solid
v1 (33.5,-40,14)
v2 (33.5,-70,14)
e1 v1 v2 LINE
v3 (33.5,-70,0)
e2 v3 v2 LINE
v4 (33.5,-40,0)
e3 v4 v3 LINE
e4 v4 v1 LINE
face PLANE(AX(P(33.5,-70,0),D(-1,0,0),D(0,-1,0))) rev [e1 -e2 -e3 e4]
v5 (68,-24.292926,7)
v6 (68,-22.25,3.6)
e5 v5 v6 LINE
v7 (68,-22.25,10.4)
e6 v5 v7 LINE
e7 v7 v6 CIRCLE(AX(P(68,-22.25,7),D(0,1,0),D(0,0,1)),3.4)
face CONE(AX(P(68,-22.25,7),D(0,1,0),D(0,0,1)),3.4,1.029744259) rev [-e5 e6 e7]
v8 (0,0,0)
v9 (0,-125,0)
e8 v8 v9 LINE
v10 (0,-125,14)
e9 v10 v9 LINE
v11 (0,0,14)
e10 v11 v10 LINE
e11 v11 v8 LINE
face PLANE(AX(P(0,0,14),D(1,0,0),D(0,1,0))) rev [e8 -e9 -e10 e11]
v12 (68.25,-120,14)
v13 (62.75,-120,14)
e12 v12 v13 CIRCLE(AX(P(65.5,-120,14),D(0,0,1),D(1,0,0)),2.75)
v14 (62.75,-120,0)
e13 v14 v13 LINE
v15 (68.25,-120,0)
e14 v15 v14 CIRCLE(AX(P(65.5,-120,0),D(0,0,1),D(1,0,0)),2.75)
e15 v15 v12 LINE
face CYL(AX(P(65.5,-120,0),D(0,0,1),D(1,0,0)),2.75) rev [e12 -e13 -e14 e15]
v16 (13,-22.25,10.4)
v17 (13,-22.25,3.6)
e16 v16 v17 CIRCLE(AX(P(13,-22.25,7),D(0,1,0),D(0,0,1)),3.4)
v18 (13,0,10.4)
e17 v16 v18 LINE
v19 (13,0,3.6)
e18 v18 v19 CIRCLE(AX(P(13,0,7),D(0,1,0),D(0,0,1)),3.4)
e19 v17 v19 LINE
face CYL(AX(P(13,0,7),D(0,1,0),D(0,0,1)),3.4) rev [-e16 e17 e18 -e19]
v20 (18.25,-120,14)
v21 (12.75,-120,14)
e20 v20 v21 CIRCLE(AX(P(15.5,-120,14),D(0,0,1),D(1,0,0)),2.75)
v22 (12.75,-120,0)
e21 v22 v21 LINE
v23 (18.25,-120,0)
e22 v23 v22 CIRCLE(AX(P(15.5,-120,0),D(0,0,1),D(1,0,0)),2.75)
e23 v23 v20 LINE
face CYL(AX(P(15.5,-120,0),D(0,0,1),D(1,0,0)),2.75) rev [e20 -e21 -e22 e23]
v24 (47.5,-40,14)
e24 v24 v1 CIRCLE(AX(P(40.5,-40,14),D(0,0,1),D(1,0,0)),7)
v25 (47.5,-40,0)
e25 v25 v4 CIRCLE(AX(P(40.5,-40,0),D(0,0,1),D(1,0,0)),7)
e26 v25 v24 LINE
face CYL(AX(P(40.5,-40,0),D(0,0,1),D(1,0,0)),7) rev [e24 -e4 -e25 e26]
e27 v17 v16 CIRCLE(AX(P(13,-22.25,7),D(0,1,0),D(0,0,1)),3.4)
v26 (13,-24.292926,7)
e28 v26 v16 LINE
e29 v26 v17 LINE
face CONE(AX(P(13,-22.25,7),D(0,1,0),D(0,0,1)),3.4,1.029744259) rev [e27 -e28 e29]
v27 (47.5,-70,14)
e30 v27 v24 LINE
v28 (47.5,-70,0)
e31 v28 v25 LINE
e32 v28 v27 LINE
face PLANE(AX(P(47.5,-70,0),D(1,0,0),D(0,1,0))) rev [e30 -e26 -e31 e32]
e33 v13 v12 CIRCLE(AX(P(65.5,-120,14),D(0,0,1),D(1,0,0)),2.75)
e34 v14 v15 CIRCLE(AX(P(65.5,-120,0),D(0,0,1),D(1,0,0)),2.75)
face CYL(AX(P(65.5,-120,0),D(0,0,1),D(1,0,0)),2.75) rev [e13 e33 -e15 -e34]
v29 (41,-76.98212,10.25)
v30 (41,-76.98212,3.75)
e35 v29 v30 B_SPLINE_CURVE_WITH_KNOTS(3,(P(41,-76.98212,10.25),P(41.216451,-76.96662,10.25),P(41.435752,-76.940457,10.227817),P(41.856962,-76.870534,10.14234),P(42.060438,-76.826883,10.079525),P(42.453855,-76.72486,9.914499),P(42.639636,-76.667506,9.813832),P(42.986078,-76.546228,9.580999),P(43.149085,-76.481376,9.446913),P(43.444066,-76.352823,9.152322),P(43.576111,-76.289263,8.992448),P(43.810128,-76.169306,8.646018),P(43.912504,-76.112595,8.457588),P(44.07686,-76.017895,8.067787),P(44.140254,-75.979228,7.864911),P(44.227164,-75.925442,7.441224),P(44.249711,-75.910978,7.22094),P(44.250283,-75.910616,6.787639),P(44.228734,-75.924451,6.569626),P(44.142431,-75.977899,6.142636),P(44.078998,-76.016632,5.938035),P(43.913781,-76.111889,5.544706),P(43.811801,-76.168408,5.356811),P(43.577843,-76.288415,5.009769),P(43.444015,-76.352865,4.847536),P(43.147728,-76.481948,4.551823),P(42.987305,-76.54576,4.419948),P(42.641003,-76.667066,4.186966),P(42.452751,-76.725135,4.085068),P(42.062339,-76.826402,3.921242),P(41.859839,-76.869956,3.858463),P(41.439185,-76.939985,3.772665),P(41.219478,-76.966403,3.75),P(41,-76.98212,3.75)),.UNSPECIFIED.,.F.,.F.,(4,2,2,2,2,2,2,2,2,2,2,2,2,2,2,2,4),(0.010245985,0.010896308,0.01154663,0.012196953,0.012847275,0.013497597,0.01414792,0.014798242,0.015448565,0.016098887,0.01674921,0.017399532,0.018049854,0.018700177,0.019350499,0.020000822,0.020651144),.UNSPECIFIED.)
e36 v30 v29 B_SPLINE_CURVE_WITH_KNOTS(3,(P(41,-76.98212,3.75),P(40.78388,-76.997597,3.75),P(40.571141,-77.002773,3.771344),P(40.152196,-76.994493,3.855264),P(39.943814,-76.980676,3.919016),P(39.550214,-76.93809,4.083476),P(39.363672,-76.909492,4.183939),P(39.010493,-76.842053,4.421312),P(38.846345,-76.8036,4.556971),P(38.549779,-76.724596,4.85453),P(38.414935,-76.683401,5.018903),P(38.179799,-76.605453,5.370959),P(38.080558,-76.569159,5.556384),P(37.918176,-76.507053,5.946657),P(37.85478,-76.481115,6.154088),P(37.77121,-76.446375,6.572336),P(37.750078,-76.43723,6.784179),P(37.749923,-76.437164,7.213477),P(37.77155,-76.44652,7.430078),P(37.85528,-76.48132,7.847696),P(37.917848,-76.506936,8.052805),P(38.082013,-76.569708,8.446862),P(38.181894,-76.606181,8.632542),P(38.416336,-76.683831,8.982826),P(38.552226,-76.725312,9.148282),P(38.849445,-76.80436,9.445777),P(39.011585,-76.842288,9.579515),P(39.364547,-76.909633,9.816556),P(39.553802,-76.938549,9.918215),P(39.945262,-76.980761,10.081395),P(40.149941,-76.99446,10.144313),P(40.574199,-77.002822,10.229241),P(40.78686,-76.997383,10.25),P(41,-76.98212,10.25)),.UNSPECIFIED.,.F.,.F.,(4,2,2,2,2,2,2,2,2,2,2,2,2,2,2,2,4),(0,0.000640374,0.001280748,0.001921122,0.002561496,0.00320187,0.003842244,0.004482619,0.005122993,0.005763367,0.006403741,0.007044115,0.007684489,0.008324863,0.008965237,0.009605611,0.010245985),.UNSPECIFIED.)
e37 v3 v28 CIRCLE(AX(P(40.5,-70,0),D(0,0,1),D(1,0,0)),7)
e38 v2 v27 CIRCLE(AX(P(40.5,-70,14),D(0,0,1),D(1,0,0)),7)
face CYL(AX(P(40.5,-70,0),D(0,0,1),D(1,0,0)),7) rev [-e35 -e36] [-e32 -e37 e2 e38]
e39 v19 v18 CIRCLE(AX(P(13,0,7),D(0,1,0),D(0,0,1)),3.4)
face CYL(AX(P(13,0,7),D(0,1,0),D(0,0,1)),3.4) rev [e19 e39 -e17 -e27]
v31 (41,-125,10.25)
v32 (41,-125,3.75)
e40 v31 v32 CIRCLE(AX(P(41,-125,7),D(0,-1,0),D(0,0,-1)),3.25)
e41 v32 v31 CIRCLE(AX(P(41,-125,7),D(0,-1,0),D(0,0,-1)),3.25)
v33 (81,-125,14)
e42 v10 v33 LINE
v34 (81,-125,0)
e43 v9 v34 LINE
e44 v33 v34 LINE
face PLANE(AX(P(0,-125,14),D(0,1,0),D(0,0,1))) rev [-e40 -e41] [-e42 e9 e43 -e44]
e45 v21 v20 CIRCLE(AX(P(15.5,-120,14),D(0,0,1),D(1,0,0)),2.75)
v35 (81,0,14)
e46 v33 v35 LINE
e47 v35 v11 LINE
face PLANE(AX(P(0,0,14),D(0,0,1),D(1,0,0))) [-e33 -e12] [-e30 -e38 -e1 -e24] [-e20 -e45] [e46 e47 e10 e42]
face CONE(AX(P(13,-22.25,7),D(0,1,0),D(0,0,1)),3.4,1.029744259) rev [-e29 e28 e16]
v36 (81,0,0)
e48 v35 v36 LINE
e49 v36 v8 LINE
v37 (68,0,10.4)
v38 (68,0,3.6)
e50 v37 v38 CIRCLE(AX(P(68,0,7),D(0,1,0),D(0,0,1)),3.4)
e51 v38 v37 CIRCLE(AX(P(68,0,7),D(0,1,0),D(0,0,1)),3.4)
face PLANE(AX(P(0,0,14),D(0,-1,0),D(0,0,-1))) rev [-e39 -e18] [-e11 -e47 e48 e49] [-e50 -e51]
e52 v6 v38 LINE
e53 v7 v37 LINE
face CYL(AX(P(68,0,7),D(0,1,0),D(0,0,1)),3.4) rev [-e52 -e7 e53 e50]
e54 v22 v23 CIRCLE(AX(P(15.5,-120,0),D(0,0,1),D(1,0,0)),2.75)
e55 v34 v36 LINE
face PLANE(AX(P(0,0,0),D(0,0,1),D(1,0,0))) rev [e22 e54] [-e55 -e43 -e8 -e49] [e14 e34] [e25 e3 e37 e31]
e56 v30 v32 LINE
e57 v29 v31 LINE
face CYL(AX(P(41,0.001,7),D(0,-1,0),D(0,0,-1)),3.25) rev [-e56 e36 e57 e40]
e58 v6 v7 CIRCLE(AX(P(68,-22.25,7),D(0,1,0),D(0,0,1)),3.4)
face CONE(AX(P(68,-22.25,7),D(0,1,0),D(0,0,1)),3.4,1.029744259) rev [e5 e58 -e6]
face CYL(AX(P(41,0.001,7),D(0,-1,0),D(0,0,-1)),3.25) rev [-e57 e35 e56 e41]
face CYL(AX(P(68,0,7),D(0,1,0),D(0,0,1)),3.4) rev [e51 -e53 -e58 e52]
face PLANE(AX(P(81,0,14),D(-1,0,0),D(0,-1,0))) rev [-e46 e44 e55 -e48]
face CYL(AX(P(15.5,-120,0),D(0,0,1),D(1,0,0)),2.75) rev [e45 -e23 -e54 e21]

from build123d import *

# Parameters (mm, degrees)
SKETCH_1_W               = 81
SKETCH_1_H               = 125
EXTRUDE_1_DEPTH          = 14
CUT_EXTRUDE_1_DEPTH      = 150.606149606
CUT_EXTRUDE_2_REACH      = 145.948
CUT_EXTRUDE_2_END_RADIUS = 7
SKETCH_4_R               = 3.25
HOLE_WIZARD_M8_1_D       = 6.8
HOLE_WIZARD_M8_1_DEPTH   = 22.25
HOLE_WIZARD_M8_1_TIP     = 2.042926105
SKETCH_11_R              = 2.75
CUT_EXTRUDE_3_DEPTH      = 150.606149699


with BuildPart() as part:
    # 草图1 → 凸台-拉伸1 (new body)
    with BuildSketch(Plane.XY):
        with Locations((40.5, -62.5)):
            Rectangle(SKETCH_1_W, SKETCH_1_H)
    extrude(amount=EXTRUDE_1_DEPTH)

    # 草图2 → 切除-拉伸1 (cut, through all)
    with BuildSketch(Plane.XY.offset(14)):
        with BuildLine():
            Line((33.5, -70), (33.5, -40))
            ThreePointArc((33.5, -40), (40.5, -33), (47.5, -40))
            Line((47.5, -40), (47.5, -70))
            ThreePointArc((47.5, -70), (40.5, -77), (33.5, -70))
        make_face()
    extrude(amount=-CUT_EXTRUDE_1_DEPTH, mode=Mode.SUBTRACT)

    # 切除-拉伸2: up to this cylinder (the profile starts outside it)
    cut_extrude_2_end = Plane(origin=(40.5, -70, 7), z_dir=(0, 0, 1)) * Cylinder(CUT_EXTRUDE_2_END_RADIUS, 306.896, mode=Mode.PRIVATE)
    # 草图4 → 切除-拉伸2 (cut, up to the surface)
    with BuildSketch(Plane(origin=(70, -125, 0), x_dir=(0, 0, -1), z_dir=(0, -1, 0)), mode=Mode.PRIVATE) as cut_extrude_2_sk1:
        with Locations((-7, -29)):
            Circle(SKETCH_4_R)
    cut_extrude_2_tool1 = extrude(cut_extrude_2_sk1.sketch, amount=-CUT_EXTRUDE_2_REACH, mode=Mode.PRIVATE) - cut_extrude_2_end
    add(cut_extrude_2_tool1.solids().sort_by_distance((41, -125, 7))[0], mode=Mode.SUBTRACT)

    # M8 螺纹孔1
    with Locations(Plane(origin=(0, 0, 0), x_dir=(1, 0, 0), z_dir=(0, 1, 0))):
        with Locations((68, -7), (13, -7)):
            Hole(HOLE_WIZARD_M8_1_D / 2, depth=HOLE_WIZARD_M8_1_DEPTH)
            with Locations((0, 0, -(HOLE_WIZARD_M8_1_DEPTH + HOLE_WIZARD_M8_1_TIP / 2))):  # 118° drill point
                Cone(0, HOLE_WIZARD_M8_1_D / 2, HOLE_WIZARD_M8_1_TIP, mode=Mode.SUBTRACT)

    # 草图11 → 切除-拉伸3 (cut, through all)
    with BuildSketch(Plane.XY.offset(14)):
        with Locations((15.5, -120)):
            Circle(SKETCH_11_R)
        with Locations((65.5, -120)):
            Circle(SKETCH_11_R)
    extrude(amount=-CUT_EXTRUDE_3_DEPTH, mode=Mode.SUBTRACT)


solid = part.part
